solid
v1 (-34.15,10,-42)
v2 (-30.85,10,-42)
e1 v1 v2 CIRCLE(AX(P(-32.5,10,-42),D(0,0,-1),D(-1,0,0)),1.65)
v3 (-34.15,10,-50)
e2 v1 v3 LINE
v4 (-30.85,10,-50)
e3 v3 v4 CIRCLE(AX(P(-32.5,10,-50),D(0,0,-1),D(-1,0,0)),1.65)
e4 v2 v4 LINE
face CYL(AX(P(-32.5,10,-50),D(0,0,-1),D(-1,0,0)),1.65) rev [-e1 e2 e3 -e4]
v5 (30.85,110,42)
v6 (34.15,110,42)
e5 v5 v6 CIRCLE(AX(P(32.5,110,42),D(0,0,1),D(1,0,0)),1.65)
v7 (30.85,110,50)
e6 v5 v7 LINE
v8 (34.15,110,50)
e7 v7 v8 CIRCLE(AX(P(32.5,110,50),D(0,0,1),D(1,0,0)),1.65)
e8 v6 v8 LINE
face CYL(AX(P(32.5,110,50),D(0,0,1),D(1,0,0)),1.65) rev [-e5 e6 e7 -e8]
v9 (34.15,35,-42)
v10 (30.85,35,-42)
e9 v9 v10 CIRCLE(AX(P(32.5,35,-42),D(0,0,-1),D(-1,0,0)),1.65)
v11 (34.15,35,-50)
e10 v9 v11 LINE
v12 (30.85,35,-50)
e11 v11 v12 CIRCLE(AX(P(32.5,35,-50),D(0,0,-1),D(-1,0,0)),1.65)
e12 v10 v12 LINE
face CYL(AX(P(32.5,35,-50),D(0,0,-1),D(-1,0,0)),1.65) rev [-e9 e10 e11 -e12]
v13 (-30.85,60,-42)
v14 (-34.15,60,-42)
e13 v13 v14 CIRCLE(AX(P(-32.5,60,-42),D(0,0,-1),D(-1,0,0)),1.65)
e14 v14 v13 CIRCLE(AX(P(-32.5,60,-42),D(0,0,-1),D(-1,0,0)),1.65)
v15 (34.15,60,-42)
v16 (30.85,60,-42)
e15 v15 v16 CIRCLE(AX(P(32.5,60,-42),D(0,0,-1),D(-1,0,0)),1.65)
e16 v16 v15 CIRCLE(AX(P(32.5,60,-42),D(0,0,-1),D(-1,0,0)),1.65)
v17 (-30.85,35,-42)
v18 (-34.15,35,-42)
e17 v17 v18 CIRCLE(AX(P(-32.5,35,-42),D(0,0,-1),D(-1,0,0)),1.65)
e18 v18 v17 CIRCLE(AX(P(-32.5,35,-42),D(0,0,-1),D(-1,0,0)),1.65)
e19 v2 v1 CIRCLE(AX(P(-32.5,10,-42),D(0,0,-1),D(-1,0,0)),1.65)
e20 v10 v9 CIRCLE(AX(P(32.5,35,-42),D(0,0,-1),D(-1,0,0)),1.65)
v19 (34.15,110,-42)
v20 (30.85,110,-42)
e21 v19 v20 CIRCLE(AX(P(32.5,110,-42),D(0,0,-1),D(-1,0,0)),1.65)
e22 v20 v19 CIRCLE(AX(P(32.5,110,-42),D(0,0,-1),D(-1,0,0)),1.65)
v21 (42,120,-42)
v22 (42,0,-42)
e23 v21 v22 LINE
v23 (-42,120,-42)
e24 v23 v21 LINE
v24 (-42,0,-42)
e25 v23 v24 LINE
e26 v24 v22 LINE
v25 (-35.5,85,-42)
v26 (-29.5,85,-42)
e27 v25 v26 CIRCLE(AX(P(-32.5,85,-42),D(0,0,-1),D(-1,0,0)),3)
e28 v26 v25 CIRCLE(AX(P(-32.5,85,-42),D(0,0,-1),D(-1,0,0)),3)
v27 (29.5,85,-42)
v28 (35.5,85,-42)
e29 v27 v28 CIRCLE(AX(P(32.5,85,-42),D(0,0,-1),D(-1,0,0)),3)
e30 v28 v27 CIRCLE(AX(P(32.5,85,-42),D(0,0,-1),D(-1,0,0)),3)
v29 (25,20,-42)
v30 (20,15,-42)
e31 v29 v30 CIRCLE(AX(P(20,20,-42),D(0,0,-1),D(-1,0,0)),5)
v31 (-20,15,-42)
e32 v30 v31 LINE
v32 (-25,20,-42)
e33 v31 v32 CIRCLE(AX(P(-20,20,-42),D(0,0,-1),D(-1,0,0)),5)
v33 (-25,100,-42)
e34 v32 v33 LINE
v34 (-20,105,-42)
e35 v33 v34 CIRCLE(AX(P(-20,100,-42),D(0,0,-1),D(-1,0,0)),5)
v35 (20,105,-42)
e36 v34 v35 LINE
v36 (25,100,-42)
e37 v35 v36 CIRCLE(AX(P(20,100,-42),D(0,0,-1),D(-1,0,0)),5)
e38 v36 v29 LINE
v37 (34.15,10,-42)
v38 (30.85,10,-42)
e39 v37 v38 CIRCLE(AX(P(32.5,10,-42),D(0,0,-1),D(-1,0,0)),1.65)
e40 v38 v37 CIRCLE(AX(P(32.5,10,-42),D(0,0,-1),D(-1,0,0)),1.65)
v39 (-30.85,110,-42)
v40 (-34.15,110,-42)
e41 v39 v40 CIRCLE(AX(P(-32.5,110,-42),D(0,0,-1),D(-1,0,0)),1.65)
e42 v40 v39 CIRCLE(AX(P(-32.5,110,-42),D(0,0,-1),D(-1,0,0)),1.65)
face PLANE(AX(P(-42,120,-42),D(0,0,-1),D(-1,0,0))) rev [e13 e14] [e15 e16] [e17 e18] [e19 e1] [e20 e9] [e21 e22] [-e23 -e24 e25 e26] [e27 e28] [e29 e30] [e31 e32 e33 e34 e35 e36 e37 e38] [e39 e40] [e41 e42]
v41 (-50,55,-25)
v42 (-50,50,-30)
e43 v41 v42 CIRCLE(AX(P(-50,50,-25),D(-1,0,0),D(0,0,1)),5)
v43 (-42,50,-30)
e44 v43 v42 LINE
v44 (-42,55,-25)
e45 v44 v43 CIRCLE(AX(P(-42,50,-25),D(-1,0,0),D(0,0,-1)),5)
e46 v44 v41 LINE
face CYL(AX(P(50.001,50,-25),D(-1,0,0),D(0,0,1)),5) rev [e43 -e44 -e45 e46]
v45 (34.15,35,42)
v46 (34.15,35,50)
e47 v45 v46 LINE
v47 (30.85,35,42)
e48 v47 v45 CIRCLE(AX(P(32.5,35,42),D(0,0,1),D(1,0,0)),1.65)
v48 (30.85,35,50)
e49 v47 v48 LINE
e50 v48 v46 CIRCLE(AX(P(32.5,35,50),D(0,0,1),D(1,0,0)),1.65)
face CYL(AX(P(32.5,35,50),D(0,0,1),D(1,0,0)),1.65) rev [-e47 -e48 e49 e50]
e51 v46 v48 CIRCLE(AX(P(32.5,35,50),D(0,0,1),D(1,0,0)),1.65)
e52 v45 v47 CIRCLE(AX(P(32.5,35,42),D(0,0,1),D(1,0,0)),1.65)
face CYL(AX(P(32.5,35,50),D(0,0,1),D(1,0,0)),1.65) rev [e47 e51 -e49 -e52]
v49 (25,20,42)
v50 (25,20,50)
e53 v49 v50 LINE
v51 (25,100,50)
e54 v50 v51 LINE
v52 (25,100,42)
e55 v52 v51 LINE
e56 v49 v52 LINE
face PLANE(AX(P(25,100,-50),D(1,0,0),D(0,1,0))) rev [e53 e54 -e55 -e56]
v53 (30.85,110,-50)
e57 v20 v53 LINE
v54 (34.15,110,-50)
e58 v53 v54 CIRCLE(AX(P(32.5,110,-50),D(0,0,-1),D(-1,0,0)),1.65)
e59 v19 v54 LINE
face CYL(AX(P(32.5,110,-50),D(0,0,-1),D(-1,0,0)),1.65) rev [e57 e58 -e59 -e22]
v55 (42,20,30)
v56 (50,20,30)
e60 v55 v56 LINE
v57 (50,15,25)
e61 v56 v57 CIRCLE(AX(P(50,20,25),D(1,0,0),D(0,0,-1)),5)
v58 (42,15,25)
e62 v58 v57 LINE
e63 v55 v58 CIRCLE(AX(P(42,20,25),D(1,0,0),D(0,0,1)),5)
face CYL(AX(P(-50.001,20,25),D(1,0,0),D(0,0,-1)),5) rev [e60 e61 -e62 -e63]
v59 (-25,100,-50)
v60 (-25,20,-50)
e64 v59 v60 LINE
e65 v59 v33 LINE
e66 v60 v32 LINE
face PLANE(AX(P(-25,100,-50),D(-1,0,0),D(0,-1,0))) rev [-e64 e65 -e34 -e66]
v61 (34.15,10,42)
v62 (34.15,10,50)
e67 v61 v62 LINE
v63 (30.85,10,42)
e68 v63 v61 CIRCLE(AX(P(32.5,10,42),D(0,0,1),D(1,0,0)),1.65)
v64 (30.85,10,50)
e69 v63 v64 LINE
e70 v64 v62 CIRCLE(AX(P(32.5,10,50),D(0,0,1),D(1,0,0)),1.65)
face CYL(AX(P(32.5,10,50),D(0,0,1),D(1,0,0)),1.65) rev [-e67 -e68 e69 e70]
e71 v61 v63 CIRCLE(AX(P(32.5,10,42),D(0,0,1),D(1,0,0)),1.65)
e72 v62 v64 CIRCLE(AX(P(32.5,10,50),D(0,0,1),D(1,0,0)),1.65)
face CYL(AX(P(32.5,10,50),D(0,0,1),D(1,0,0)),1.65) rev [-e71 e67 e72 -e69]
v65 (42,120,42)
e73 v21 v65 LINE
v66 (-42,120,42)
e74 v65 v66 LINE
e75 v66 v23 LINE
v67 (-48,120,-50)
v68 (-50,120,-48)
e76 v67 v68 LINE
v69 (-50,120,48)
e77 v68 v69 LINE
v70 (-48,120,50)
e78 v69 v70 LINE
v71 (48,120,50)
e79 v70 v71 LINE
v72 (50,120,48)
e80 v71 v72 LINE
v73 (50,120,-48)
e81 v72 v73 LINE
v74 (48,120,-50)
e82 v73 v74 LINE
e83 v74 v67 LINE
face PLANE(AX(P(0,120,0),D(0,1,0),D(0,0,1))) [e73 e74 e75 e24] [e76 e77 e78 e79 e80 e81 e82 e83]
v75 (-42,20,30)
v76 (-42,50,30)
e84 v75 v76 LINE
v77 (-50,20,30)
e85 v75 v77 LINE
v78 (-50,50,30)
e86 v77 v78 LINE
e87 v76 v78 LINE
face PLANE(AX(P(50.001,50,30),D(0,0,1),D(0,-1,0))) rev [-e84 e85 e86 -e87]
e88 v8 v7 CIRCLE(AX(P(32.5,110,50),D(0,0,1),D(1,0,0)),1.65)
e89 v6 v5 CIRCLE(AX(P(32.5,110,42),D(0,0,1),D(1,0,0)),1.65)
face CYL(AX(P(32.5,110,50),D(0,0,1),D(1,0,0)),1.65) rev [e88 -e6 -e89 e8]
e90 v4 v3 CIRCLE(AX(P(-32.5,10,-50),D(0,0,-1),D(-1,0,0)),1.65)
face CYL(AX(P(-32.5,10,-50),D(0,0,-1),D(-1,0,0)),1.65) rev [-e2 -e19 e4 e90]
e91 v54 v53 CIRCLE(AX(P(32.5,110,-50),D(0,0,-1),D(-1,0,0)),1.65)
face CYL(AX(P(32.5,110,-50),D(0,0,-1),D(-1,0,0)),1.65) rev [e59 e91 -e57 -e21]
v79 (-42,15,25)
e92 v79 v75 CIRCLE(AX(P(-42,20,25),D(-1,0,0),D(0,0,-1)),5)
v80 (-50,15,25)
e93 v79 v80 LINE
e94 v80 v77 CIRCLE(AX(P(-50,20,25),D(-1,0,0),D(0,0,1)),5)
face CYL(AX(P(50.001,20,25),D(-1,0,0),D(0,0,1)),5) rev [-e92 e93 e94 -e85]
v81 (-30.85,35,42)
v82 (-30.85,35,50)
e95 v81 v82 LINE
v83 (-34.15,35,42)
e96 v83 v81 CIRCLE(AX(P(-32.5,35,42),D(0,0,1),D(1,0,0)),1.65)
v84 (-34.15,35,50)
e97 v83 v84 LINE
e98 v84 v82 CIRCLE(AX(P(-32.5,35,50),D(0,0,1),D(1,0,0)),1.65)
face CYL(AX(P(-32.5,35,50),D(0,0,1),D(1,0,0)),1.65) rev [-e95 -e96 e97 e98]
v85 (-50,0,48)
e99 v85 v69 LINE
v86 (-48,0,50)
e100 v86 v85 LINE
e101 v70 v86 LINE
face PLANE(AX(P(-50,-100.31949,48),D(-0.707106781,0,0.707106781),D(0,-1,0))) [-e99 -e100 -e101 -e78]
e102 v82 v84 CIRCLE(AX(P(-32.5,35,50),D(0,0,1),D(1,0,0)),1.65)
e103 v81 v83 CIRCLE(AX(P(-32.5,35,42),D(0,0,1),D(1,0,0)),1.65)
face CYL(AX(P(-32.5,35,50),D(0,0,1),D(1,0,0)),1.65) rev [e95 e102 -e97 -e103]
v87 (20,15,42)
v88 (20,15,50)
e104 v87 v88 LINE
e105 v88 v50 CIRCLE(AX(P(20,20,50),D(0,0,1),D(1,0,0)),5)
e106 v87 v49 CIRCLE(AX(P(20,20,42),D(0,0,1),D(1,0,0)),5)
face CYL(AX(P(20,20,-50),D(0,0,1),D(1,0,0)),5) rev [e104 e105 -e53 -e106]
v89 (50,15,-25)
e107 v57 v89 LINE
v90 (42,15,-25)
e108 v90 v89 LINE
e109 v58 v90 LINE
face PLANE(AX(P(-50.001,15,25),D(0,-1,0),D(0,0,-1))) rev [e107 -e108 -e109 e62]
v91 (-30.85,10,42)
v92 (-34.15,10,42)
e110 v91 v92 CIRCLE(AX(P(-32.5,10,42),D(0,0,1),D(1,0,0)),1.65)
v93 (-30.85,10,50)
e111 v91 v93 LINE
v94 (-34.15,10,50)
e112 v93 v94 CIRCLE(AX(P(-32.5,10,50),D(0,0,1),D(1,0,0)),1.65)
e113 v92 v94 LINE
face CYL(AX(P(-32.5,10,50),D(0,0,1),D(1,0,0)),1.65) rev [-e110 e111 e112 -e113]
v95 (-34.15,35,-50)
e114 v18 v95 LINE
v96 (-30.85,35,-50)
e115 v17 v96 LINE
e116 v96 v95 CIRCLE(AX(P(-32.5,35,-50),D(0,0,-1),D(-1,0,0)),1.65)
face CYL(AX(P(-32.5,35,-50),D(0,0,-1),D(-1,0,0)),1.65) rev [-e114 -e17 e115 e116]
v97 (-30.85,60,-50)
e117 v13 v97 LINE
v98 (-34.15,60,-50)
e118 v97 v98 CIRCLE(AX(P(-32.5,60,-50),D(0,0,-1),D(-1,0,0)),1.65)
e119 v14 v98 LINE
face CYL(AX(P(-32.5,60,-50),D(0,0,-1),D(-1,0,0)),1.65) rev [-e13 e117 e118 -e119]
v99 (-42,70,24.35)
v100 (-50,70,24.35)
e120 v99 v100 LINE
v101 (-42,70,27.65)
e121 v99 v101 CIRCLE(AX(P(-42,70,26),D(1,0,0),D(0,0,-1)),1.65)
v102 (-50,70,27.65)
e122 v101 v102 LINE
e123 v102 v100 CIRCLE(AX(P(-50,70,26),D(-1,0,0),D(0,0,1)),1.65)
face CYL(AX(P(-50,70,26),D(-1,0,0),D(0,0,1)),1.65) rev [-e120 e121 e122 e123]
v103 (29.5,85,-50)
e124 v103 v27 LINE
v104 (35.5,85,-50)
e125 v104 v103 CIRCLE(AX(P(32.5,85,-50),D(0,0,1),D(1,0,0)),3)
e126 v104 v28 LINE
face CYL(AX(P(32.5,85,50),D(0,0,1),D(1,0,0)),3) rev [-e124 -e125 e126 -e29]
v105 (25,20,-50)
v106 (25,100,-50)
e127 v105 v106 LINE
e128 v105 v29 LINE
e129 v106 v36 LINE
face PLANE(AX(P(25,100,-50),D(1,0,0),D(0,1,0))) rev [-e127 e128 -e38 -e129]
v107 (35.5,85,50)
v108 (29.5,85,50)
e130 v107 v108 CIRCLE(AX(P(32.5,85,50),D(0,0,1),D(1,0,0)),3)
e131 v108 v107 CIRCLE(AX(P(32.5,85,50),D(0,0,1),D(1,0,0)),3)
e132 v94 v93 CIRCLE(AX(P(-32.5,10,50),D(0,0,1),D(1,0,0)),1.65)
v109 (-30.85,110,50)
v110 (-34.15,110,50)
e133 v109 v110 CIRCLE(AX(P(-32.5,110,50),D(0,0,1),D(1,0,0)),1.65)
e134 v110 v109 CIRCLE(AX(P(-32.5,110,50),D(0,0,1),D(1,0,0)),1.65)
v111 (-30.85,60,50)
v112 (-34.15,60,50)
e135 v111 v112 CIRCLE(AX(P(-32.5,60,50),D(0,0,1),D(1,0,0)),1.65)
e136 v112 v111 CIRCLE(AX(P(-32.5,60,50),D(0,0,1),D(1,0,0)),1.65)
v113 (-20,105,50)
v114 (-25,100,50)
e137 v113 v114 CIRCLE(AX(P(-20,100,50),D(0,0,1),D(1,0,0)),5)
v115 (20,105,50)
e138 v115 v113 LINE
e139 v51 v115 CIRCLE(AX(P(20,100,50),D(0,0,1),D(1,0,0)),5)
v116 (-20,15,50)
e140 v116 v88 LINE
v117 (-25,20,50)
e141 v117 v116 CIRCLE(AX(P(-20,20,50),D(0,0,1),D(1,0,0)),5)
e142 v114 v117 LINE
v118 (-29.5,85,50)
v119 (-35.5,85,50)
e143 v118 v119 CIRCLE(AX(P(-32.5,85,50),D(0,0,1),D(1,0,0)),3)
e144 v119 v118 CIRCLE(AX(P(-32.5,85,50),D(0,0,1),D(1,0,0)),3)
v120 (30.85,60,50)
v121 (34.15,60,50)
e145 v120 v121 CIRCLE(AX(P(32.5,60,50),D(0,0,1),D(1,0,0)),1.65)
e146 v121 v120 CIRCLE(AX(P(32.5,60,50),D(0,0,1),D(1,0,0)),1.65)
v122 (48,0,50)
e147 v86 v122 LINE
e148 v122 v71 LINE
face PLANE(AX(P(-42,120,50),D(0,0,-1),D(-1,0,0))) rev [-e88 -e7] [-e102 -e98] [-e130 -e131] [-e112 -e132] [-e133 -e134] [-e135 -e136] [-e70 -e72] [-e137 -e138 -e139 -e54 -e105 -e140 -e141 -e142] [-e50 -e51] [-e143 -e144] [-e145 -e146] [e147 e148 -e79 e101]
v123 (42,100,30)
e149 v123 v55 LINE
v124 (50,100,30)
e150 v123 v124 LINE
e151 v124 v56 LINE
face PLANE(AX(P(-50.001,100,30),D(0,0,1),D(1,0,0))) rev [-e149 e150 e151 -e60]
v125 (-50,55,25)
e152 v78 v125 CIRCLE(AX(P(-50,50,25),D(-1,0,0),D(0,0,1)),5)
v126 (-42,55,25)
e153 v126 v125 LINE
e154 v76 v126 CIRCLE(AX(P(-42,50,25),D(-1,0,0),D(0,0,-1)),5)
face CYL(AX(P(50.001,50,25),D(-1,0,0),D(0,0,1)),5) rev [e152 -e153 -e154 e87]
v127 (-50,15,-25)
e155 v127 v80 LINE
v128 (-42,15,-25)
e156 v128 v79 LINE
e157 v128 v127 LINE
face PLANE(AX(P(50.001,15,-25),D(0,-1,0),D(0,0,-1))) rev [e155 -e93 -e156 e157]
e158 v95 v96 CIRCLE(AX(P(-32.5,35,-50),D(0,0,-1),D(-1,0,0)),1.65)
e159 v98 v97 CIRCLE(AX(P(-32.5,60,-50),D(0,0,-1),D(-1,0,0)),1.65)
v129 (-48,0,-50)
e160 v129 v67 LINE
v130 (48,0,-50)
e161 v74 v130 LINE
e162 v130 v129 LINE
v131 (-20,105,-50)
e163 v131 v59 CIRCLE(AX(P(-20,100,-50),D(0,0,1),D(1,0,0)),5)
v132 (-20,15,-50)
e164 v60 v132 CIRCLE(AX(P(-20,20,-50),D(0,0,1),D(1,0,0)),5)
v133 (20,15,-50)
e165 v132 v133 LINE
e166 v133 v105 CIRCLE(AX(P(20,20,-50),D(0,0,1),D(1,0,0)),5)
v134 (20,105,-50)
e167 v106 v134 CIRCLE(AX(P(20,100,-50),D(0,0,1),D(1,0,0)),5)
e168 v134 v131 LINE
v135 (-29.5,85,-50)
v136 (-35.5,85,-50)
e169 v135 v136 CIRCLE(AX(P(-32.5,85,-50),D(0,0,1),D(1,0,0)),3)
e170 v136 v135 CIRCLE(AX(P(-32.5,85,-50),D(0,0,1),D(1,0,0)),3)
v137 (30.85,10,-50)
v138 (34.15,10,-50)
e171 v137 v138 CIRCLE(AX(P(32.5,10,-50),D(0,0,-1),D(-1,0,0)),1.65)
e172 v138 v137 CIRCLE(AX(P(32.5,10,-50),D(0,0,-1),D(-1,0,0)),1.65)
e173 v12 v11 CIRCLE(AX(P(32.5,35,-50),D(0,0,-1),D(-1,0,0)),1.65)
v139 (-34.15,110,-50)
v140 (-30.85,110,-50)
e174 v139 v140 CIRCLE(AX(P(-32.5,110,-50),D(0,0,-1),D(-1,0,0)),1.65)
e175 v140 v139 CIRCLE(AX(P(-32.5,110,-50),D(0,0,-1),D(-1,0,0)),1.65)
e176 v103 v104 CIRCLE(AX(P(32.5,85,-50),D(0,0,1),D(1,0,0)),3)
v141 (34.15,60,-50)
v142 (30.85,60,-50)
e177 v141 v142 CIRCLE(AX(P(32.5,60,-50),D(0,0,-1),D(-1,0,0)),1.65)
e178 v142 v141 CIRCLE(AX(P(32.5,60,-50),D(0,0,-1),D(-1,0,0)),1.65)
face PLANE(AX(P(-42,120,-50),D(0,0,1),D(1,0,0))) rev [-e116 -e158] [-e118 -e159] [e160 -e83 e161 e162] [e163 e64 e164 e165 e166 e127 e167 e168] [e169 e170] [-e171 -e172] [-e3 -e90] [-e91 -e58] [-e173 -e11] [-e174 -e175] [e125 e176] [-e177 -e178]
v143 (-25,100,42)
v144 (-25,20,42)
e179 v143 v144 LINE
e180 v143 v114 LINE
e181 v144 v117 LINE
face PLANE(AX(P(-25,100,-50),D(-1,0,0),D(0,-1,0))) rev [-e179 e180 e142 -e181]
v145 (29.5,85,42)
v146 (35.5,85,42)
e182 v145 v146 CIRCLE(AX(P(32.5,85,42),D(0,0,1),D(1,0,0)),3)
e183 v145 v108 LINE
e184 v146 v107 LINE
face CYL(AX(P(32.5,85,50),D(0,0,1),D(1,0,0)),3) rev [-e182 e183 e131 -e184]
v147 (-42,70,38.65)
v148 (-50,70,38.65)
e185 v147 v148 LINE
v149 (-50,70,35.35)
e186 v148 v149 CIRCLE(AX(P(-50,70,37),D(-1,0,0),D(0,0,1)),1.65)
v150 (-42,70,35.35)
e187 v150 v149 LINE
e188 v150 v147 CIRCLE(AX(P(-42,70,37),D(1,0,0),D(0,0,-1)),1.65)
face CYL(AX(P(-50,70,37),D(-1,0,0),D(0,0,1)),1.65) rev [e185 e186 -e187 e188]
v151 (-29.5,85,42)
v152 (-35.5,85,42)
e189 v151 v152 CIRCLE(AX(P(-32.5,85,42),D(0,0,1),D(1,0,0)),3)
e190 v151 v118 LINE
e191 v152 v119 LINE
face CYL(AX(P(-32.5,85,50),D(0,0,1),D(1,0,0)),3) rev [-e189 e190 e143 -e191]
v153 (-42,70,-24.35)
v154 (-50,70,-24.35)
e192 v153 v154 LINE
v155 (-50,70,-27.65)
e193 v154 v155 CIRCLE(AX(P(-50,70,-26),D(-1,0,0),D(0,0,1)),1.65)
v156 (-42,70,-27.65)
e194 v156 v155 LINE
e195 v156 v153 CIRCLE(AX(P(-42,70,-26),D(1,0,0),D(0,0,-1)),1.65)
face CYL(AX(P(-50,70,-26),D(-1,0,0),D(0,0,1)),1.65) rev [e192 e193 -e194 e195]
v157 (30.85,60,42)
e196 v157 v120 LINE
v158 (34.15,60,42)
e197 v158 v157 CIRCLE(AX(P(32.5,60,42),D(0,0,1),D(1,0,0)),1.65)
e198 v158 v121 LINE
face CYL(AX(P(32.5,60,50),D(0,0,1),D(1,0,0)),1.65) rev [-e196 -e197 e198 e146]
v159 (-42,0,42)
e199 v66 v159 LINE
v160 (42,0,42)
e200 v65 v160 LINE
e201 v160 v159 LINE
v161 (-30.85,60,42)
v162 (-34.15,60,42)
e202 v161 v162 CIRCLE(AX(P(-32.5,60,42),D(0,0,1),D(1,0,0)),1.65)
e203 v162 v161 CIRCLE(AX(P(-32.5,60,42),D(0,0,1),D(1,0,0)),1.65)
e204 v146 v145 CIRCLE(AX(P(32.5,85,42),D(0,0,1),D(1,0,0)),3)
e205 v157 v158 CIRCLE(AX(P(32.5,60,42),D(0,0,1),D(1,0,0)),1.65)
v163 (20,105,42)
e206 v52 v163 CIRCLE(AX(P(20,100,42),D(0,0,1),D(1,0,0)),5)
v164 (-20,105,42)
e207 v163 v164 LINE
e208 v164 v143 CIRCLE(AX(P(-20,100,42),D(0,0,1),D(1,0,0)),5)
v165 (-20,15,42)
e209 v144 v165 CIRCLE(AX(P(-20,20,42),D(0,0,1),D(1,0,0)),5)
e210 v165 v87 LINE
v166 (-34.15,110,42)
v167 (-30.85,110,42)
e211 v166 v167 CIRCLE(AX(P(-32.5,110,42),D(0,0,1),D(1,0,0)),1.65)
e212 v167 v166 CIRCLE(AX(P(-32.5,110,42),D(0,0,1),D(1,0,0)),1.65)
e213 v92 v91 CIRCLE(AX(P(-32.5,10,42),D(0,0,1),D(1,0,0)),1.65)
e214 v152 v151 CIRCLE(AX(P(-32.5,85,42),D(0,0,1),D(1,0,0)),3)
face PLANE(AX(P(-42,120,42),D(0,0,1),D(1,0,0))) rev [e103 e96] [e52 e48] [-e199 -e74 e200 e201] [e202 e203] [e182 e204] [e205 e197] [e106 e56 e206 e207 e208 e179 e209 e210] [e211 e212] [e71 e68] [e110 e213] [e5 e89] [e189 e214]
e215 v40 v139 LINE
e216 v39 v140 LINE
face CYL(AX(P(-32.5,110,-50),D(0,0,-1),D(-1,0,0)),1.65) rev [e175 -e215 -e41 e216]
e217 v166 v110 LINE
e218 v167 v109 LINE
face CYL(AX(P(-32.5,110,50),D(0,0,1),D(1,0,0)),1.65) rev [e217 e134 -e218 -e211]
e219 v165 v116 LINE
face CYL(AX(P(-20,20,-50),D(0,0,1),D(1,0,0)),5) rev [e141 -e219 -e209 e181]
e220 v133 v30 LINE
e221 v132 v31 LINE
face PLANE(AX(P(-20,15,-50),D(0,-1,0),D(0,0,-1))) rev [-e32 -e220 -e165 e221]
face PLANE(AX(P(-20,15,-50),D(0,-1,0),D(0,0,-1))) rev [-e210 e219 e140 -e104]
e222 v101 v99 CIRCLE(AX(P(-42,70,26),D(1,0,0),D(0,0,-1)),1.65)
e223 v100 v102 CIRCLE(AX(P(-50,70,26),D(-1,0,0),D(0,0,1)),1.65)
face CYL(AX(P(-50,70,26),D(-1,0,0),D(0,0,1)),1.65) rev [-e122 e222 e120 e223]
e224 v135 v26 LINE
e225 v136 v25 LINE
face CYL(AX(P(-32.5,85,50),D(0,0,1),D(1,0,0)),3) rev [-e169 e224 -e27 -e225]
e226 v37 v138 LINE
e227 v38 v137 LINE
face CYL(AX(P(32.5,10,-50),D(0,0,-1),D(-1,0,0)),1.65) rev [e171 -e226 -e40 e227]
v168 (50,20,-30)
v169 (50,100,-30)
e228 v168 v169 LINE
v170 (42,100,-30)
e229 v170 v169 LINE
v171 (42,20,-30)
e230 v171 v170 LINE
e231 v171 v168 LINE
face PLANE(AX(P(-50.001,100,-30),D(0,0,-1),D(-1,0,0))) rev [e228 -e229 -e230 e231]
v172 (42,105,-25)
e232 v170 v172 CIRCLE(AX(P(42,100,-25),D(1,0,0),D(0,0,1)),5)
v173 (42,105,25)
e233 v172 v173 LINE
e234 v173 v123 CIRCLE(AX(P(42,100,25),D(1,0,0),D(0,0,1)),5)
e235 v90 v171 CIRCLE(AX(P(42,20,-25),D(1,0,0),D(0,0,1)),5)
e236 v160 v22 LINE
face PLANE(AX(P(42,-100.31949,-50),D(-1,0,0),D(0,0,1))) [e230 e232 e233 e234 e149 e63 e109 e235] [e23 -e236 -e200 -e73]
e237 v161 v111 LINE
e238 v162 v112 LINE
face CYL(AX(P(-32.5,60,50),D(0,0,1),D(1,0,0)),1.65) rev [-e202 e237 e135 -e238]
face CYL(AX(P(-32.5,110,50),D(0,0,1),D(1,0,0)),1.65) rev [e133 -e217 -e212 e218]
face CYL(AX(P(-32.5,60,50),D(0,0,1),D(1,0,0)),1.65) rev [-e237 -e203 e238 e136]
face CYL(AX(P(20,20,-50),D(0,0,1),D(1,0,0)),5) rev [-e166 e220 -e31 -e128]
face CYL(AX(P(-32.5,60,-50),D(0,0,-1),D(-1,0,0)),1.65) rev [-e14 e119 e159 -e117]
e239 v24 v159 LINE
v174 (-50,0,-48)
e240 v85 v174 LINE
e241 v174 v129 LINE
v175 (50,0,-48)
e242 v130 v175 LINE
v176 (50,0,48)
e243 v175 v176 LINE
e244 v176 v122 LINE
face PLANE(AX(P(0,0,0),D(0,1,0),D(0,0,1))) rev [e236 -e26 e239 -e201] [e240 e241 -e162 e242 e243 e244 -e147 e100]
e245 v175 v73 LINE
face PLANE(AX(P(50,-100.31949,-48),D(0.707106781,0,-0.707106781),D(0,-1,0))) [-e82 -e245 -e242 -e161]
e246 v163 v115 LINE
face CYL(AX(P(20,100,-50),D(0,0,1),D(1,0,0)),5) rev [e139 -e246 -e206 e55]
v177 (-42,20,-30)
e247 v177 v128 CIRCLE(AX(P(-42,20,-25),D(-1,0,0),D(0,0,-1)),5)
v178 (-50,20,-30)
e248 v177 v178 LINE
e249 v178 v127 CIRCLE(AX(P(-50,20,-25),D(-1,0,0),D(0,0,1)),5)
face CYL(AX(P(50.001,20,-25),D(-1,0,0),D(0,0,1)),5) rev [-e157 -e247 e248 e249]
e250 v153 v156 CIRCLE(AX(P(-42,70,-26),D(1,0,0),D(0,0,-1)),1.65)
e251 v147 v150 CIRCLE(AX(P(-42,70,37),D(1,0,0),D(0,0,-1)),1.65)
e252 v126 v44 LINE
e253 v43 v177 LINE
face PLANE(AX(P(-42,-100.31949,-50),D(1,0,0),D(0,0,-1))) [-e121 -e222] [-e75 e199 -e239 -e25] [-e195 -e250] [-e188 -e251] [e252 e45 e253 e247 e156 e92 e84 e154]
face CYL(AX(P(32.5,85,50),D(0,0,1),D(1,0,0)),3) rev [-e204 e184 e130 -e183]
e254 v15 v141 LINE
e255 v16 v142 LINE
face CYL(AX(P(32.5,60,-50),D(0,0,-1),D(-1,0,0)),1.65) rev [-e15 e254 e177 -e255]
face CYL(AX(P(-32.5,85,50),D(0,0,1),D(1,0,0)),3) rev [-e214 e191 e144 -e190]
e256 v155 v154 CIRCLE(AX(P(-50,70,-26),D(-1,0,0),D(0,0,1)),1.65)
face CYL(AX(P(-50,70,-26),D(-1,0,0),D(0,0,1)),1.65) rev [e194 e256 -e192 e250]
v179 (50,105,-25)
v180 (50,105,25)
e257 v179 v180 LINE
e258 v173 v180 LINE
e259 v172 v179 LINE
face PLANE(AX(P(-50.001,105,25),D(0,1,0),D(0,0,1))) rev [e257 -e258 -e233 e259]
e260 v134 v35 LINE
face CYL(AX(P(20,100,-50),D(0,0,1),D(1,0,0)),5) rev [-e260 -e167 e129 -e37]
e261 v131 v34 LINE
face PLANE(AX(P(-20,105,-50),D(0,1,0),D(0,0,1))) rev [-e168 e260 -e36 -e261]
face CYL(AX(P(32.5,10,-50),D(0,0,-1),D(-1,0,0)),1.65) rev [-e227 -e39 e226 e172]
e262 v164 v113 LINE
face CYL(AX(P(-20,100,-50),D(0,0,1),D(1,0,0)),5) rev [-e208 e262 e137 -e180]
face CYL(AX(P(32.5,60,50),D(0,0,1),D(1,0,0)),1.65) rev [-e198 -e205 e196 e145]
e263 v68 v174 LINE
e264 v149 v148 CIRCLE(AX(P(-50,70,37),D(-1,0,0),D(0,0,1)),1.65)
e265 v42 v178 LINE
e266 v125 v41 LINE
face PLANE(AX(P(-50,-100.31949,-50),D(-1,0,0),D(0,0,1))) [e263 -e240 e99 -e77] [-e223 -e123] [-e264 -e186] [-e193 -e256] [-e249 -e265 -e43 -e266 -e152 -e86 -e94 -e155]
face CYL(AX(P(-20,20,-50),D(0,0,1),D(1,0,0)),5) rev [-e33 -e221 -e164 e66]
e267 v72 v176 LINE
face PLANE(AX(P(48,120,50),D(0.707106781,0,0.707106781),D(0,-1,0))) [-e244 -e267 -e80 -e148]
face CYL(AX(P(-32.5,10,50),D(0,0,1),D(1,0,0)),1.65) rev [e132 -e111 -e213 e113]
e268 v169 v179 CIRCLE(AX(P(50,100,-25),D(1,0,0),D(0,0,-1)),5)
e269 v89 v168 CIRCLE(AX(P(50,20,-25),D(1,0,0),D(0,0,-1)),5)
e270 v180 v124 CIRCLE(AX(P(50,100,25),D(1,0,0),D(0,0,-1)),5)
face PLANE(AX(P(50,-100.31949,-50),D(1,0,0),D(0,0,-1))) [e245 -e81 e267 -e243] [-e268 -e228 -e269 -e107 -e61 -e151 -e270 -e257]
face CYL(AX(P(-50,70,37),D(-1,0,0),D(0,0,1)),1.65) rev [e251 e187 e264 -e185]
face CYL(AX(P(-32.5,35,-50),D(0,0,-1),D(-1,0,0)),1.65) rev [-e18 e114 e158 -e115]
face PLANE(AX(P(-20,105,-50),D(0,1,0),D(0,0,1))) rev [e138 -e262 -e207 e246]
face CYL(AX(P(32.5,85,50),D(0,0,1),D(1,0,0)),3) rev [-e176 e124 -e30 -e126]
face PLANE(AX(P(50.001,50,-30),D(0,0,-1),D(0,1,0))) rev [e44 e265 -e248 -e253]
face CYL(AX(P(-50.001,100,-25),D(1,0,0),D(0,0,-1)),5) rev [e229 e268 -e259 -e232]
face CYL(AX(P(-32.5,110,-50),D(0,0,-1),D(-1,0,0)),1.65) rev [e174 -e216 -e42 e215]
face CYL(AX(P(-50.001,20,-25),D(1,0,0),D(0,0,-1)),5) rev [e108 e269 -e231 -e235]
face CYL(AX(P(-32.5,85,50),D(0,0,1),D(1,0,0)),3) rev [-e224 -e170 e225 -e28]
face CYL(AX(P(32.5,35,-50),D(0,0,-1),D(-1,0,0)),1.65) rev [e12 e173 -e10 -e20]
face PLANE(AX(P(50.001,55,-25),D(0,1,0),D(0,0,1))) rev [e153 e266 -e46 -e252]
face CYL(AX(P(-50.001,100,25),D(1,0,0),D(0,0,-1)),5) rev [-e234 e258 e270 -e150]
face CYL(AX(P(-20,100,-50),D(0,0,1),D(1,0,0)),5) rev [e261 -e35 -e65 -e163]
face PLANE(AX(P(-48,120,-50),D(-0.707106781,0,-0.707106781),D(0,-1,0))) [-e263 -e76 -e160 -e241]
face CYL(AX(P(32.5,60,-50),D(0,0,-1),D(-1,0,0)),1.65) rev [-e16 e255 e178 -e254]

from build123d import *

# Parameters (mm, degrees)
BOSS_EXTRUDE1_DEPTH        = 120
SKETCH3_W                  = 8
SKETCH3_H                  = 100
BOSS_EXTRUDE2_DEPTH        = 120
SKETCH4_W                  = 84
SKETCH4_H                  = 84
CUT_EXTRUDE2_DEPTH         = 140.283882772
SKETCH6_R                  = 1.034396221
SKETCH6_R_2                = 1
CUT_EXTRUDE4_DEPTH         = 7
M4_TAPPED_HOLE1_AT_2_COUNT = 2
M4_TAPPED_HOLE1_AT_2_PITCH = 65
M4_TAPPED_HOLE1_AT_3_COUNT = 2
M4_TAPPED_HOLE1_AT_3_PITCH = 119.268604419
M4_TAPPED_HOLE1_AT_4_COUNT = 2
M4_TAPPED_HOLE1_AT_4_PITCH = 100
M4_TAPPED_HOLE1_AT_5_COUNT = 2
M4_TAPPED_HOLE1_AT_5_PITCH = 50
M4_TAPPED_HOLE1_AT_6_COUNT = 2
M4_TAPPED_HOLE1_AT_6_PITCH = 82.006097334
M4_TAPPED_HOLE2_D          = 3.3
M4_TAPPED_HOLE2_DEPTH      = 11.5
M4_TAPPED_HOLE2_TIP        = 0.991420021
F_6_0_6_DIAMETER_HOLE1_D   = 6
CUT_EXTRUDE5_DEPTH         = 165.012194669
CUT_EXTRUDE6_REACH         = 166.012
CUT_EXTRUDE7_REACH         = 166.012
M4_TAPPED_HOLE3_REACH      = 166.012
M4_TAPPED_HOLE3_BORE_R     = 1.65
CHAMFER1_SIZE              = 2


with BuildPart() as part:
    # Sketch1 → Boss-Extrude1 (new body)
    with BuildSketch(Plane(origin=(0, 0, 0), x_dir=(1, 0, 0), z_dir=(0, 1, 0))):
        Polygon((-42, 50), (42, 50), (42, 42), (3, 42), (3, -42), (42, -42), (42, -50), (-42, -50), (-42, -42), (-3, -42), (-3, 42), (-42, 42), align=None)
    extrude(amount=BOSS_EXTRUDE1_DEPTH)

    # Sketch3 → Boss-Extrude2 (add)
    with BuildSketch(Plane(origin=(0, 120, 0), x_dir=(1, 0, 0), z_dir=(0, 1, 0))):
        with Locations((-46, 0)):
            Rectangle(SKETCH3_W, SKETCH3_H)
        with Locations((46, 0)):
            Rectangle(SKETCH3_W, SKETCH3_H)
    extrude(amount=-BOSS_EXTRUDE2_DEPTH)

    # Sketch4 → Cut-Extrude2 (cut, through all)
    with BuildSketch(Plane(origin=(0, 120, 0), x_dir=(1, 0, 0), z_dir=(0, 1, 0))):
        Rectangle(SKETCH4_W, SKETCH4_H)
    extrude(amount=-CUT_EXTRUDE2_DEPTH, mode=Mode.SUBTRACT)

    # Sketch6 → Cut-Extrude4 (cut)
    with BuildSketch(Plane.XY.offset(50)):
        with Locations((-32.5, 60)):
            Circle(SKETCH6_R)
        with Locations(Location((32.5, 60, 0), (0, 0, 180))):
            Circle(SKETCH6_R)
        with Locations((-32.5, 110)):
            Circle(SKETCH6_R_2)
        with Locations(Location((32.5, 110, 0), (0, 0, 180))):
            Circle(SKETCH6_R_2)
        with Locations((32.5, 10)):
            Circle(SKETCH6_R_2)
        with Locations(Location((-32.5, 10, 0), (0, 0, 180))):
            Circle(SKETCH6_R_2)
    extrude(amount=-CUT_EXTRUDE4_DEPTH, mode=Mode.SUBTRACT)

    # Sketch7 → M4 Tapped Hole1 (revolve, cut)
    with BuildSketch(Plane(origin=(-32.5, 110, 50), x_dir=(0, -1, 0), z_dir=(1, 0, 0))):
        Polygon((0, 0), (0, 11.091420021), (1.65, 10.1), (1.65, 0), align=None)
    m4_tapped_hole1 = revolve(axis=Axis((-32.5, 110, 56.35), (0, 0, -1)), mode=Mode.SUBTRACT)

    # M4 Tapped Hole1 at 2: M4 Tapped Hole1 ×2
    with Locations(*[(i * M4_TAPPED_HOLE1_AT_2_PITCH, 0, 0) for i in range(1, M4_TAPPED_HOLE1_AT_2_COUNT)]):
        add(m4_tapped_hole1, mode=Mode.SUBTRACT)

    # M4 Tapped Hole1 at 3: M4 Tapped Hole1 ×2
    with Locations(*[Vector(0.5449883505954143, -0.8384436163006371, 0) * (i * M4_TAPPED_HOLE1_AT_3_PITCH) for i in range(1, M4_TAPPED_HOLE1_AT_3_COUNT)]):
        add(m4_tapped_hole1, mode=Mode.SUBTRACT)

    # M4 Tapped Hole1 at 4: M4 Tapped Hole1 ×2
    with Locations(*[(0, -i * M4_TAPPED_HOLE1_AT_4_PITCH, 0) for i in range(1, M4_TAPPED_HOLE1_AT_4_COUNT)]):
        add(m4_tapped_hole1, mode=Mode.SUBTRACT)

    # M4 Tapped Hole1 at 5: M4 Tapped Hole1 ×2
    with Locations(*[(0, -i * M4_TAPPED_HOLE1_AT_5_PITCH, 0) for i in range(1, M4_TAPPED_HOLE1_AT_5_COUNT)]):
        add(m4_tapped_hole1, mode=Mode.SUBTRACT)

    # M4 Tapped Hole1 at 6: M4 Tapped Hole1 ×2
    with Locations(*[Vector(0.7926239891046003, -0.6097107608496921, 0) * (i * M4_TAPPED_HOLE1_AT_6_PITCH) for i in range(1, M4_TAPPED_HOLE1_AT_6_COUNT)]):
        add(m4_tapped_hole1, mode=Mode.SUBTRACT)

    # Mirror2: M4 Tapped Hole1 across plane
    add(m4_tapped_hole1.mirror(Plane.XY), mode=Mode.SUBTRACT)

    # Mirror2 copy 1 sketch → Mirror2 copy 1 (revolve, cut)
    with BuildSketch(Plane(origin=(32.5, 110, -50), x_dir=(0, -1, 0), z_dir=(1, 0, 0))):
        Polygon((0, 0), (0, -11.091420021), (1.65, -10.1), (1.65, 0), align=None)
    revolve(axis=Axis((32.5, 110, -56.35), (0, 0, -1)), mode=Mode.SUBTRACT)

    # Mirror2 copy 2 sketch → Mirror2 copy 2 (revolve, cut)
    with BuildSketch(Plane(origin=(32.5, 10, -50), x_dir=(0, -1, 0), z_dir=(1, 0, 0))):
        Polygon((0, 0), (0, -11.091420021), (1.65, -10.1), (1.65, 0), align=None)
    revolve(axis=Axis((32.5, 10, -56.35), (0, 0, -1)), mode=Mode.SUBTRACT)

    # Mirror2 copy 3 sketch → Mirror2 copy 3 (revolve, cut)
    with BuildSketch(Plane(origin=(-32.5, 10, -50), x_dir=(0, -1, 0), z_dir=(1, 0, 0))):
        Polygon((0, 0), (0, -11.091420021), (1.65, -10.1), (1.65, 0), align=None)
    revolve(axis=Axis((-32.5, 10, -56.35), (0, 0, -1)), mode=Mode.SUBTRACT)

    # Mirror2 copy 4 sketch → Mirror2 copy 4 (revolve, cut)
    with BuildSketch(Plane(origin=(-32.5, 60, -50), x_dir=(0, -1, 0), z_dir=(1, 0, 0))):
        Polygon((0, 0), (0, -11.091420021), (1.65, -10.1), (1.65, 0), align=None)
    revolve(axis=Axis((-32.5, 60, -56.35), (0, 0, -1)), mode=Mode.SUBTRACT)

    # Mirror2 copy 5 sketch → Mirror2 copy 5 (revolve, cut)
    with BuildSketch(Plane(origin=(32.5, 60, -50), x_dir=(0, -1, 0), z_dir=(1, 0, 0))):
        Polygon((0, 0), (0, -11.091420021), (1.65, -10.1), (1.65, 0), align=None)
    revolve(axis=Axis((32.5, 60, -56.35), (0, 0, -1)), mode=Mode.SUBTRACT)

    # M4 Tapped Hole2
    with Locations(Plane.ZY.offset(50)):
        with Locations((-26, 70), (26, 70), (37, 70)):
            Hole(M4_TAPPED_HOLE2_D / 2, depth=M4_TAPPED_HOLE2_DEPTH)
            with Locations((0, 0, -(M4_TAPPED_HOLE2_DEPTH + M4_TAPPED_HOLE2_TIP / 2))):  # 118° drill point
                Cone(0, M4_TAPPED_HOLE2_D / 2, M4_TAPPED_HOLE2_TIP, mode=Mode.SUBTRACT)

    # Ø6.0 (6) Diameter Hole1 (through all)
    with Locations(Plane.XY.offset(50)):
        with Locations((-32.5, 85), (32.5, 85)):
            Hole(F_6_0_6_DIAMETER_HOLE1_D / 2)

    # Sketch12 → Cut-Extrude5 (cut, through all)
    with BuildSketch(Plane.XY.offset(50)):
        with BuildLine():
            Line((-20, 105), (20, 105))
            ThreePointArc((20, 105), (23.535533906, 103.535533906), (25, 100))
            Line((25, 100), (25, 20))
            ThreePointArc((25, 20), (23.535533906, 16.464466094), (20, 15))
            Line((20, 15), (-20, 15))
            ThreePointArc((-20, 15), (-23.535533906, 16.464466094), (-25, 20))
            Line((-25, 20), (-25, 100))
            ThreePointArc((-25, 100), (-23.535533906, 103.535533906), (-20, 105))
        make_face()
    extrude(amount=-CUT_EXTRUDE5_DEPTH, mode=Mode.SUBTRACT)

    # Sketch13 → Cut-Extrude6 (cut, up to next)
    with BuildSketch(Plane(origin=(50, 0, 0), x_dir=(0, 0, -1), z_dir=(1, 0, 0)), mode=Mode.PRIVATE) as cut_extrude6_sk1:
        with BuildLine():
            Line((-25, 105), (25, 105))
            ThreePointArc((25, 105), (28.535533906, 103.535533906), (30, 100))
            Line((30, 100), (30, 20))
            ThreePointArc((30, 20), (28.535533906, 16.464466094), (25, 15))
            Line((25, 15), (-25, 15))
            ThreePointArc((-25, 15), (-28.535533906, 16.464466094), (-30, 20))
            Line((-30, 20), (-30, 100))
            ThreePointArc((-30, 100), (-28.535533906, 103.535533906), (-25, 105))
        make_face()
    cut_extrude6_tool1 = extrude(cut_extrude6_sk1.sketch, amount=-CUT_EXTRUDE6_REACH, mode=Mode.PRIVATE) & part.part
    add(cut_extrude6_tool1.solids().sort_by_distance((50, 60, 0))[0], mode=Mode.SUBTRACT)

    # Sketch14 → Cut-Extrude7 (cut, up to next)
    with BuildSketch(Plane.ZY.offset(50), mode=Mode.PRIVATE) as cut_extrude7_sk1:
        with BuildLine():
            Line((-25, 55), (25, 55))
            ThreePointArc((25, 55), (28.535533906, 53.535533906), (30, 50))
            Line((30, 50), (30, 20))
            ThreePointArc((30, 20), (28.535533906, 16.464466094), (25, 15))
            Line((25, 15), (-25, 15))
            ThreePointArc((-25, 15), (-28.535533906, 16.464466094), (-30, 20))
            Line((-30, 20), (-30, 50))
            ThreePointArc((-30, 50), (-28.535533906, 53.535533906), (-25, 55))
        make_face()
    cut_extrude7_tool1 = extrude(cut_extrude7_sk1.sketch, amount=-CUT_EXTRUDE7_REACH, mode=Mode.PRIVATE) & part.part
    add(cut_extrude7_tool1.solids().sort_by_distance((-50, 35, 0))[0], mode=Mode.SUBTRACT)

    # M4 Tapped Hole3 bore → M4 Tapped Hole3 (cut, up to next)
    with BuildSketch(Plane.XY.offset(50), mode=Mode.PRIVATE) as m4_tapped_hole3_sk1:
        with Locations((-32.5, 35)):
            Circle(M4_TAPPED_HOLE3_BORE_R)
    m4_tapped_hole3_tool1 = extrude(m4_tapped_hole3_sk1.sketch, amount=-M4_TAPPED_HOLE3_REACH, mode=Mode.PRIVATE) & part.part
    # M4 Tapped Hole3 bore → M4 Tapped Hole3 (cut, up to next)
    with BuildSketch(Plane.XY.offset(50), mode=Mode.PRIVATE) as m4_tapped_hole3_sk2:
        with Locations((32.5, 35)):
            Circle(M4_TAPPED_HOLE3_BORE_R)
    m4_tapped_hole3_tool2 = extrude(m4_tapped_hole3_sk2.sketch, amount=-M4_TAPPED_HOLE3_REACH, mode=Mode.PRIVATE) & part.part
    m4_tapped_hole3_1 = m4_tapped_hole3_tool1.solids().sort_by_distance((-32.5, 35, 50))[0]
    add(m4_tapped_hole3_1, mode=Mode.SUBTRACT)
    m4_tapped_hole3_2 = m4_tapped_hole3_tool2.solids().sort_by_distance((32.5, 35, 50))[0]
    add(m4_tapped_hole3_2, mode=Mode.SUBTRACT)
    m4_tapped_hole3 = m4_tapped_hole3_1 + m4_tapped_hole3_2  # M4 Tapped Hole3 as one shape, for the pattern or mirror that repeats it

    # Mirror3: M4 Tapped Hole3 across plane
    add(m4_tapped_hole3.mirror(Plane.XY), mode=Mode.SUBTRACT)

    # Chamfer1
    chamfer1_edges = [part.edges().sort_by_distance(p)[0] for p in [
        (-50, 60, 50),
        (-50, 60, -50),
        (50, 60, -50),
        (50, 60, 50),
    ]]
    chamfer(chamfer1_edges, length=CHAMFER1_SIZE)


solid = part.part
